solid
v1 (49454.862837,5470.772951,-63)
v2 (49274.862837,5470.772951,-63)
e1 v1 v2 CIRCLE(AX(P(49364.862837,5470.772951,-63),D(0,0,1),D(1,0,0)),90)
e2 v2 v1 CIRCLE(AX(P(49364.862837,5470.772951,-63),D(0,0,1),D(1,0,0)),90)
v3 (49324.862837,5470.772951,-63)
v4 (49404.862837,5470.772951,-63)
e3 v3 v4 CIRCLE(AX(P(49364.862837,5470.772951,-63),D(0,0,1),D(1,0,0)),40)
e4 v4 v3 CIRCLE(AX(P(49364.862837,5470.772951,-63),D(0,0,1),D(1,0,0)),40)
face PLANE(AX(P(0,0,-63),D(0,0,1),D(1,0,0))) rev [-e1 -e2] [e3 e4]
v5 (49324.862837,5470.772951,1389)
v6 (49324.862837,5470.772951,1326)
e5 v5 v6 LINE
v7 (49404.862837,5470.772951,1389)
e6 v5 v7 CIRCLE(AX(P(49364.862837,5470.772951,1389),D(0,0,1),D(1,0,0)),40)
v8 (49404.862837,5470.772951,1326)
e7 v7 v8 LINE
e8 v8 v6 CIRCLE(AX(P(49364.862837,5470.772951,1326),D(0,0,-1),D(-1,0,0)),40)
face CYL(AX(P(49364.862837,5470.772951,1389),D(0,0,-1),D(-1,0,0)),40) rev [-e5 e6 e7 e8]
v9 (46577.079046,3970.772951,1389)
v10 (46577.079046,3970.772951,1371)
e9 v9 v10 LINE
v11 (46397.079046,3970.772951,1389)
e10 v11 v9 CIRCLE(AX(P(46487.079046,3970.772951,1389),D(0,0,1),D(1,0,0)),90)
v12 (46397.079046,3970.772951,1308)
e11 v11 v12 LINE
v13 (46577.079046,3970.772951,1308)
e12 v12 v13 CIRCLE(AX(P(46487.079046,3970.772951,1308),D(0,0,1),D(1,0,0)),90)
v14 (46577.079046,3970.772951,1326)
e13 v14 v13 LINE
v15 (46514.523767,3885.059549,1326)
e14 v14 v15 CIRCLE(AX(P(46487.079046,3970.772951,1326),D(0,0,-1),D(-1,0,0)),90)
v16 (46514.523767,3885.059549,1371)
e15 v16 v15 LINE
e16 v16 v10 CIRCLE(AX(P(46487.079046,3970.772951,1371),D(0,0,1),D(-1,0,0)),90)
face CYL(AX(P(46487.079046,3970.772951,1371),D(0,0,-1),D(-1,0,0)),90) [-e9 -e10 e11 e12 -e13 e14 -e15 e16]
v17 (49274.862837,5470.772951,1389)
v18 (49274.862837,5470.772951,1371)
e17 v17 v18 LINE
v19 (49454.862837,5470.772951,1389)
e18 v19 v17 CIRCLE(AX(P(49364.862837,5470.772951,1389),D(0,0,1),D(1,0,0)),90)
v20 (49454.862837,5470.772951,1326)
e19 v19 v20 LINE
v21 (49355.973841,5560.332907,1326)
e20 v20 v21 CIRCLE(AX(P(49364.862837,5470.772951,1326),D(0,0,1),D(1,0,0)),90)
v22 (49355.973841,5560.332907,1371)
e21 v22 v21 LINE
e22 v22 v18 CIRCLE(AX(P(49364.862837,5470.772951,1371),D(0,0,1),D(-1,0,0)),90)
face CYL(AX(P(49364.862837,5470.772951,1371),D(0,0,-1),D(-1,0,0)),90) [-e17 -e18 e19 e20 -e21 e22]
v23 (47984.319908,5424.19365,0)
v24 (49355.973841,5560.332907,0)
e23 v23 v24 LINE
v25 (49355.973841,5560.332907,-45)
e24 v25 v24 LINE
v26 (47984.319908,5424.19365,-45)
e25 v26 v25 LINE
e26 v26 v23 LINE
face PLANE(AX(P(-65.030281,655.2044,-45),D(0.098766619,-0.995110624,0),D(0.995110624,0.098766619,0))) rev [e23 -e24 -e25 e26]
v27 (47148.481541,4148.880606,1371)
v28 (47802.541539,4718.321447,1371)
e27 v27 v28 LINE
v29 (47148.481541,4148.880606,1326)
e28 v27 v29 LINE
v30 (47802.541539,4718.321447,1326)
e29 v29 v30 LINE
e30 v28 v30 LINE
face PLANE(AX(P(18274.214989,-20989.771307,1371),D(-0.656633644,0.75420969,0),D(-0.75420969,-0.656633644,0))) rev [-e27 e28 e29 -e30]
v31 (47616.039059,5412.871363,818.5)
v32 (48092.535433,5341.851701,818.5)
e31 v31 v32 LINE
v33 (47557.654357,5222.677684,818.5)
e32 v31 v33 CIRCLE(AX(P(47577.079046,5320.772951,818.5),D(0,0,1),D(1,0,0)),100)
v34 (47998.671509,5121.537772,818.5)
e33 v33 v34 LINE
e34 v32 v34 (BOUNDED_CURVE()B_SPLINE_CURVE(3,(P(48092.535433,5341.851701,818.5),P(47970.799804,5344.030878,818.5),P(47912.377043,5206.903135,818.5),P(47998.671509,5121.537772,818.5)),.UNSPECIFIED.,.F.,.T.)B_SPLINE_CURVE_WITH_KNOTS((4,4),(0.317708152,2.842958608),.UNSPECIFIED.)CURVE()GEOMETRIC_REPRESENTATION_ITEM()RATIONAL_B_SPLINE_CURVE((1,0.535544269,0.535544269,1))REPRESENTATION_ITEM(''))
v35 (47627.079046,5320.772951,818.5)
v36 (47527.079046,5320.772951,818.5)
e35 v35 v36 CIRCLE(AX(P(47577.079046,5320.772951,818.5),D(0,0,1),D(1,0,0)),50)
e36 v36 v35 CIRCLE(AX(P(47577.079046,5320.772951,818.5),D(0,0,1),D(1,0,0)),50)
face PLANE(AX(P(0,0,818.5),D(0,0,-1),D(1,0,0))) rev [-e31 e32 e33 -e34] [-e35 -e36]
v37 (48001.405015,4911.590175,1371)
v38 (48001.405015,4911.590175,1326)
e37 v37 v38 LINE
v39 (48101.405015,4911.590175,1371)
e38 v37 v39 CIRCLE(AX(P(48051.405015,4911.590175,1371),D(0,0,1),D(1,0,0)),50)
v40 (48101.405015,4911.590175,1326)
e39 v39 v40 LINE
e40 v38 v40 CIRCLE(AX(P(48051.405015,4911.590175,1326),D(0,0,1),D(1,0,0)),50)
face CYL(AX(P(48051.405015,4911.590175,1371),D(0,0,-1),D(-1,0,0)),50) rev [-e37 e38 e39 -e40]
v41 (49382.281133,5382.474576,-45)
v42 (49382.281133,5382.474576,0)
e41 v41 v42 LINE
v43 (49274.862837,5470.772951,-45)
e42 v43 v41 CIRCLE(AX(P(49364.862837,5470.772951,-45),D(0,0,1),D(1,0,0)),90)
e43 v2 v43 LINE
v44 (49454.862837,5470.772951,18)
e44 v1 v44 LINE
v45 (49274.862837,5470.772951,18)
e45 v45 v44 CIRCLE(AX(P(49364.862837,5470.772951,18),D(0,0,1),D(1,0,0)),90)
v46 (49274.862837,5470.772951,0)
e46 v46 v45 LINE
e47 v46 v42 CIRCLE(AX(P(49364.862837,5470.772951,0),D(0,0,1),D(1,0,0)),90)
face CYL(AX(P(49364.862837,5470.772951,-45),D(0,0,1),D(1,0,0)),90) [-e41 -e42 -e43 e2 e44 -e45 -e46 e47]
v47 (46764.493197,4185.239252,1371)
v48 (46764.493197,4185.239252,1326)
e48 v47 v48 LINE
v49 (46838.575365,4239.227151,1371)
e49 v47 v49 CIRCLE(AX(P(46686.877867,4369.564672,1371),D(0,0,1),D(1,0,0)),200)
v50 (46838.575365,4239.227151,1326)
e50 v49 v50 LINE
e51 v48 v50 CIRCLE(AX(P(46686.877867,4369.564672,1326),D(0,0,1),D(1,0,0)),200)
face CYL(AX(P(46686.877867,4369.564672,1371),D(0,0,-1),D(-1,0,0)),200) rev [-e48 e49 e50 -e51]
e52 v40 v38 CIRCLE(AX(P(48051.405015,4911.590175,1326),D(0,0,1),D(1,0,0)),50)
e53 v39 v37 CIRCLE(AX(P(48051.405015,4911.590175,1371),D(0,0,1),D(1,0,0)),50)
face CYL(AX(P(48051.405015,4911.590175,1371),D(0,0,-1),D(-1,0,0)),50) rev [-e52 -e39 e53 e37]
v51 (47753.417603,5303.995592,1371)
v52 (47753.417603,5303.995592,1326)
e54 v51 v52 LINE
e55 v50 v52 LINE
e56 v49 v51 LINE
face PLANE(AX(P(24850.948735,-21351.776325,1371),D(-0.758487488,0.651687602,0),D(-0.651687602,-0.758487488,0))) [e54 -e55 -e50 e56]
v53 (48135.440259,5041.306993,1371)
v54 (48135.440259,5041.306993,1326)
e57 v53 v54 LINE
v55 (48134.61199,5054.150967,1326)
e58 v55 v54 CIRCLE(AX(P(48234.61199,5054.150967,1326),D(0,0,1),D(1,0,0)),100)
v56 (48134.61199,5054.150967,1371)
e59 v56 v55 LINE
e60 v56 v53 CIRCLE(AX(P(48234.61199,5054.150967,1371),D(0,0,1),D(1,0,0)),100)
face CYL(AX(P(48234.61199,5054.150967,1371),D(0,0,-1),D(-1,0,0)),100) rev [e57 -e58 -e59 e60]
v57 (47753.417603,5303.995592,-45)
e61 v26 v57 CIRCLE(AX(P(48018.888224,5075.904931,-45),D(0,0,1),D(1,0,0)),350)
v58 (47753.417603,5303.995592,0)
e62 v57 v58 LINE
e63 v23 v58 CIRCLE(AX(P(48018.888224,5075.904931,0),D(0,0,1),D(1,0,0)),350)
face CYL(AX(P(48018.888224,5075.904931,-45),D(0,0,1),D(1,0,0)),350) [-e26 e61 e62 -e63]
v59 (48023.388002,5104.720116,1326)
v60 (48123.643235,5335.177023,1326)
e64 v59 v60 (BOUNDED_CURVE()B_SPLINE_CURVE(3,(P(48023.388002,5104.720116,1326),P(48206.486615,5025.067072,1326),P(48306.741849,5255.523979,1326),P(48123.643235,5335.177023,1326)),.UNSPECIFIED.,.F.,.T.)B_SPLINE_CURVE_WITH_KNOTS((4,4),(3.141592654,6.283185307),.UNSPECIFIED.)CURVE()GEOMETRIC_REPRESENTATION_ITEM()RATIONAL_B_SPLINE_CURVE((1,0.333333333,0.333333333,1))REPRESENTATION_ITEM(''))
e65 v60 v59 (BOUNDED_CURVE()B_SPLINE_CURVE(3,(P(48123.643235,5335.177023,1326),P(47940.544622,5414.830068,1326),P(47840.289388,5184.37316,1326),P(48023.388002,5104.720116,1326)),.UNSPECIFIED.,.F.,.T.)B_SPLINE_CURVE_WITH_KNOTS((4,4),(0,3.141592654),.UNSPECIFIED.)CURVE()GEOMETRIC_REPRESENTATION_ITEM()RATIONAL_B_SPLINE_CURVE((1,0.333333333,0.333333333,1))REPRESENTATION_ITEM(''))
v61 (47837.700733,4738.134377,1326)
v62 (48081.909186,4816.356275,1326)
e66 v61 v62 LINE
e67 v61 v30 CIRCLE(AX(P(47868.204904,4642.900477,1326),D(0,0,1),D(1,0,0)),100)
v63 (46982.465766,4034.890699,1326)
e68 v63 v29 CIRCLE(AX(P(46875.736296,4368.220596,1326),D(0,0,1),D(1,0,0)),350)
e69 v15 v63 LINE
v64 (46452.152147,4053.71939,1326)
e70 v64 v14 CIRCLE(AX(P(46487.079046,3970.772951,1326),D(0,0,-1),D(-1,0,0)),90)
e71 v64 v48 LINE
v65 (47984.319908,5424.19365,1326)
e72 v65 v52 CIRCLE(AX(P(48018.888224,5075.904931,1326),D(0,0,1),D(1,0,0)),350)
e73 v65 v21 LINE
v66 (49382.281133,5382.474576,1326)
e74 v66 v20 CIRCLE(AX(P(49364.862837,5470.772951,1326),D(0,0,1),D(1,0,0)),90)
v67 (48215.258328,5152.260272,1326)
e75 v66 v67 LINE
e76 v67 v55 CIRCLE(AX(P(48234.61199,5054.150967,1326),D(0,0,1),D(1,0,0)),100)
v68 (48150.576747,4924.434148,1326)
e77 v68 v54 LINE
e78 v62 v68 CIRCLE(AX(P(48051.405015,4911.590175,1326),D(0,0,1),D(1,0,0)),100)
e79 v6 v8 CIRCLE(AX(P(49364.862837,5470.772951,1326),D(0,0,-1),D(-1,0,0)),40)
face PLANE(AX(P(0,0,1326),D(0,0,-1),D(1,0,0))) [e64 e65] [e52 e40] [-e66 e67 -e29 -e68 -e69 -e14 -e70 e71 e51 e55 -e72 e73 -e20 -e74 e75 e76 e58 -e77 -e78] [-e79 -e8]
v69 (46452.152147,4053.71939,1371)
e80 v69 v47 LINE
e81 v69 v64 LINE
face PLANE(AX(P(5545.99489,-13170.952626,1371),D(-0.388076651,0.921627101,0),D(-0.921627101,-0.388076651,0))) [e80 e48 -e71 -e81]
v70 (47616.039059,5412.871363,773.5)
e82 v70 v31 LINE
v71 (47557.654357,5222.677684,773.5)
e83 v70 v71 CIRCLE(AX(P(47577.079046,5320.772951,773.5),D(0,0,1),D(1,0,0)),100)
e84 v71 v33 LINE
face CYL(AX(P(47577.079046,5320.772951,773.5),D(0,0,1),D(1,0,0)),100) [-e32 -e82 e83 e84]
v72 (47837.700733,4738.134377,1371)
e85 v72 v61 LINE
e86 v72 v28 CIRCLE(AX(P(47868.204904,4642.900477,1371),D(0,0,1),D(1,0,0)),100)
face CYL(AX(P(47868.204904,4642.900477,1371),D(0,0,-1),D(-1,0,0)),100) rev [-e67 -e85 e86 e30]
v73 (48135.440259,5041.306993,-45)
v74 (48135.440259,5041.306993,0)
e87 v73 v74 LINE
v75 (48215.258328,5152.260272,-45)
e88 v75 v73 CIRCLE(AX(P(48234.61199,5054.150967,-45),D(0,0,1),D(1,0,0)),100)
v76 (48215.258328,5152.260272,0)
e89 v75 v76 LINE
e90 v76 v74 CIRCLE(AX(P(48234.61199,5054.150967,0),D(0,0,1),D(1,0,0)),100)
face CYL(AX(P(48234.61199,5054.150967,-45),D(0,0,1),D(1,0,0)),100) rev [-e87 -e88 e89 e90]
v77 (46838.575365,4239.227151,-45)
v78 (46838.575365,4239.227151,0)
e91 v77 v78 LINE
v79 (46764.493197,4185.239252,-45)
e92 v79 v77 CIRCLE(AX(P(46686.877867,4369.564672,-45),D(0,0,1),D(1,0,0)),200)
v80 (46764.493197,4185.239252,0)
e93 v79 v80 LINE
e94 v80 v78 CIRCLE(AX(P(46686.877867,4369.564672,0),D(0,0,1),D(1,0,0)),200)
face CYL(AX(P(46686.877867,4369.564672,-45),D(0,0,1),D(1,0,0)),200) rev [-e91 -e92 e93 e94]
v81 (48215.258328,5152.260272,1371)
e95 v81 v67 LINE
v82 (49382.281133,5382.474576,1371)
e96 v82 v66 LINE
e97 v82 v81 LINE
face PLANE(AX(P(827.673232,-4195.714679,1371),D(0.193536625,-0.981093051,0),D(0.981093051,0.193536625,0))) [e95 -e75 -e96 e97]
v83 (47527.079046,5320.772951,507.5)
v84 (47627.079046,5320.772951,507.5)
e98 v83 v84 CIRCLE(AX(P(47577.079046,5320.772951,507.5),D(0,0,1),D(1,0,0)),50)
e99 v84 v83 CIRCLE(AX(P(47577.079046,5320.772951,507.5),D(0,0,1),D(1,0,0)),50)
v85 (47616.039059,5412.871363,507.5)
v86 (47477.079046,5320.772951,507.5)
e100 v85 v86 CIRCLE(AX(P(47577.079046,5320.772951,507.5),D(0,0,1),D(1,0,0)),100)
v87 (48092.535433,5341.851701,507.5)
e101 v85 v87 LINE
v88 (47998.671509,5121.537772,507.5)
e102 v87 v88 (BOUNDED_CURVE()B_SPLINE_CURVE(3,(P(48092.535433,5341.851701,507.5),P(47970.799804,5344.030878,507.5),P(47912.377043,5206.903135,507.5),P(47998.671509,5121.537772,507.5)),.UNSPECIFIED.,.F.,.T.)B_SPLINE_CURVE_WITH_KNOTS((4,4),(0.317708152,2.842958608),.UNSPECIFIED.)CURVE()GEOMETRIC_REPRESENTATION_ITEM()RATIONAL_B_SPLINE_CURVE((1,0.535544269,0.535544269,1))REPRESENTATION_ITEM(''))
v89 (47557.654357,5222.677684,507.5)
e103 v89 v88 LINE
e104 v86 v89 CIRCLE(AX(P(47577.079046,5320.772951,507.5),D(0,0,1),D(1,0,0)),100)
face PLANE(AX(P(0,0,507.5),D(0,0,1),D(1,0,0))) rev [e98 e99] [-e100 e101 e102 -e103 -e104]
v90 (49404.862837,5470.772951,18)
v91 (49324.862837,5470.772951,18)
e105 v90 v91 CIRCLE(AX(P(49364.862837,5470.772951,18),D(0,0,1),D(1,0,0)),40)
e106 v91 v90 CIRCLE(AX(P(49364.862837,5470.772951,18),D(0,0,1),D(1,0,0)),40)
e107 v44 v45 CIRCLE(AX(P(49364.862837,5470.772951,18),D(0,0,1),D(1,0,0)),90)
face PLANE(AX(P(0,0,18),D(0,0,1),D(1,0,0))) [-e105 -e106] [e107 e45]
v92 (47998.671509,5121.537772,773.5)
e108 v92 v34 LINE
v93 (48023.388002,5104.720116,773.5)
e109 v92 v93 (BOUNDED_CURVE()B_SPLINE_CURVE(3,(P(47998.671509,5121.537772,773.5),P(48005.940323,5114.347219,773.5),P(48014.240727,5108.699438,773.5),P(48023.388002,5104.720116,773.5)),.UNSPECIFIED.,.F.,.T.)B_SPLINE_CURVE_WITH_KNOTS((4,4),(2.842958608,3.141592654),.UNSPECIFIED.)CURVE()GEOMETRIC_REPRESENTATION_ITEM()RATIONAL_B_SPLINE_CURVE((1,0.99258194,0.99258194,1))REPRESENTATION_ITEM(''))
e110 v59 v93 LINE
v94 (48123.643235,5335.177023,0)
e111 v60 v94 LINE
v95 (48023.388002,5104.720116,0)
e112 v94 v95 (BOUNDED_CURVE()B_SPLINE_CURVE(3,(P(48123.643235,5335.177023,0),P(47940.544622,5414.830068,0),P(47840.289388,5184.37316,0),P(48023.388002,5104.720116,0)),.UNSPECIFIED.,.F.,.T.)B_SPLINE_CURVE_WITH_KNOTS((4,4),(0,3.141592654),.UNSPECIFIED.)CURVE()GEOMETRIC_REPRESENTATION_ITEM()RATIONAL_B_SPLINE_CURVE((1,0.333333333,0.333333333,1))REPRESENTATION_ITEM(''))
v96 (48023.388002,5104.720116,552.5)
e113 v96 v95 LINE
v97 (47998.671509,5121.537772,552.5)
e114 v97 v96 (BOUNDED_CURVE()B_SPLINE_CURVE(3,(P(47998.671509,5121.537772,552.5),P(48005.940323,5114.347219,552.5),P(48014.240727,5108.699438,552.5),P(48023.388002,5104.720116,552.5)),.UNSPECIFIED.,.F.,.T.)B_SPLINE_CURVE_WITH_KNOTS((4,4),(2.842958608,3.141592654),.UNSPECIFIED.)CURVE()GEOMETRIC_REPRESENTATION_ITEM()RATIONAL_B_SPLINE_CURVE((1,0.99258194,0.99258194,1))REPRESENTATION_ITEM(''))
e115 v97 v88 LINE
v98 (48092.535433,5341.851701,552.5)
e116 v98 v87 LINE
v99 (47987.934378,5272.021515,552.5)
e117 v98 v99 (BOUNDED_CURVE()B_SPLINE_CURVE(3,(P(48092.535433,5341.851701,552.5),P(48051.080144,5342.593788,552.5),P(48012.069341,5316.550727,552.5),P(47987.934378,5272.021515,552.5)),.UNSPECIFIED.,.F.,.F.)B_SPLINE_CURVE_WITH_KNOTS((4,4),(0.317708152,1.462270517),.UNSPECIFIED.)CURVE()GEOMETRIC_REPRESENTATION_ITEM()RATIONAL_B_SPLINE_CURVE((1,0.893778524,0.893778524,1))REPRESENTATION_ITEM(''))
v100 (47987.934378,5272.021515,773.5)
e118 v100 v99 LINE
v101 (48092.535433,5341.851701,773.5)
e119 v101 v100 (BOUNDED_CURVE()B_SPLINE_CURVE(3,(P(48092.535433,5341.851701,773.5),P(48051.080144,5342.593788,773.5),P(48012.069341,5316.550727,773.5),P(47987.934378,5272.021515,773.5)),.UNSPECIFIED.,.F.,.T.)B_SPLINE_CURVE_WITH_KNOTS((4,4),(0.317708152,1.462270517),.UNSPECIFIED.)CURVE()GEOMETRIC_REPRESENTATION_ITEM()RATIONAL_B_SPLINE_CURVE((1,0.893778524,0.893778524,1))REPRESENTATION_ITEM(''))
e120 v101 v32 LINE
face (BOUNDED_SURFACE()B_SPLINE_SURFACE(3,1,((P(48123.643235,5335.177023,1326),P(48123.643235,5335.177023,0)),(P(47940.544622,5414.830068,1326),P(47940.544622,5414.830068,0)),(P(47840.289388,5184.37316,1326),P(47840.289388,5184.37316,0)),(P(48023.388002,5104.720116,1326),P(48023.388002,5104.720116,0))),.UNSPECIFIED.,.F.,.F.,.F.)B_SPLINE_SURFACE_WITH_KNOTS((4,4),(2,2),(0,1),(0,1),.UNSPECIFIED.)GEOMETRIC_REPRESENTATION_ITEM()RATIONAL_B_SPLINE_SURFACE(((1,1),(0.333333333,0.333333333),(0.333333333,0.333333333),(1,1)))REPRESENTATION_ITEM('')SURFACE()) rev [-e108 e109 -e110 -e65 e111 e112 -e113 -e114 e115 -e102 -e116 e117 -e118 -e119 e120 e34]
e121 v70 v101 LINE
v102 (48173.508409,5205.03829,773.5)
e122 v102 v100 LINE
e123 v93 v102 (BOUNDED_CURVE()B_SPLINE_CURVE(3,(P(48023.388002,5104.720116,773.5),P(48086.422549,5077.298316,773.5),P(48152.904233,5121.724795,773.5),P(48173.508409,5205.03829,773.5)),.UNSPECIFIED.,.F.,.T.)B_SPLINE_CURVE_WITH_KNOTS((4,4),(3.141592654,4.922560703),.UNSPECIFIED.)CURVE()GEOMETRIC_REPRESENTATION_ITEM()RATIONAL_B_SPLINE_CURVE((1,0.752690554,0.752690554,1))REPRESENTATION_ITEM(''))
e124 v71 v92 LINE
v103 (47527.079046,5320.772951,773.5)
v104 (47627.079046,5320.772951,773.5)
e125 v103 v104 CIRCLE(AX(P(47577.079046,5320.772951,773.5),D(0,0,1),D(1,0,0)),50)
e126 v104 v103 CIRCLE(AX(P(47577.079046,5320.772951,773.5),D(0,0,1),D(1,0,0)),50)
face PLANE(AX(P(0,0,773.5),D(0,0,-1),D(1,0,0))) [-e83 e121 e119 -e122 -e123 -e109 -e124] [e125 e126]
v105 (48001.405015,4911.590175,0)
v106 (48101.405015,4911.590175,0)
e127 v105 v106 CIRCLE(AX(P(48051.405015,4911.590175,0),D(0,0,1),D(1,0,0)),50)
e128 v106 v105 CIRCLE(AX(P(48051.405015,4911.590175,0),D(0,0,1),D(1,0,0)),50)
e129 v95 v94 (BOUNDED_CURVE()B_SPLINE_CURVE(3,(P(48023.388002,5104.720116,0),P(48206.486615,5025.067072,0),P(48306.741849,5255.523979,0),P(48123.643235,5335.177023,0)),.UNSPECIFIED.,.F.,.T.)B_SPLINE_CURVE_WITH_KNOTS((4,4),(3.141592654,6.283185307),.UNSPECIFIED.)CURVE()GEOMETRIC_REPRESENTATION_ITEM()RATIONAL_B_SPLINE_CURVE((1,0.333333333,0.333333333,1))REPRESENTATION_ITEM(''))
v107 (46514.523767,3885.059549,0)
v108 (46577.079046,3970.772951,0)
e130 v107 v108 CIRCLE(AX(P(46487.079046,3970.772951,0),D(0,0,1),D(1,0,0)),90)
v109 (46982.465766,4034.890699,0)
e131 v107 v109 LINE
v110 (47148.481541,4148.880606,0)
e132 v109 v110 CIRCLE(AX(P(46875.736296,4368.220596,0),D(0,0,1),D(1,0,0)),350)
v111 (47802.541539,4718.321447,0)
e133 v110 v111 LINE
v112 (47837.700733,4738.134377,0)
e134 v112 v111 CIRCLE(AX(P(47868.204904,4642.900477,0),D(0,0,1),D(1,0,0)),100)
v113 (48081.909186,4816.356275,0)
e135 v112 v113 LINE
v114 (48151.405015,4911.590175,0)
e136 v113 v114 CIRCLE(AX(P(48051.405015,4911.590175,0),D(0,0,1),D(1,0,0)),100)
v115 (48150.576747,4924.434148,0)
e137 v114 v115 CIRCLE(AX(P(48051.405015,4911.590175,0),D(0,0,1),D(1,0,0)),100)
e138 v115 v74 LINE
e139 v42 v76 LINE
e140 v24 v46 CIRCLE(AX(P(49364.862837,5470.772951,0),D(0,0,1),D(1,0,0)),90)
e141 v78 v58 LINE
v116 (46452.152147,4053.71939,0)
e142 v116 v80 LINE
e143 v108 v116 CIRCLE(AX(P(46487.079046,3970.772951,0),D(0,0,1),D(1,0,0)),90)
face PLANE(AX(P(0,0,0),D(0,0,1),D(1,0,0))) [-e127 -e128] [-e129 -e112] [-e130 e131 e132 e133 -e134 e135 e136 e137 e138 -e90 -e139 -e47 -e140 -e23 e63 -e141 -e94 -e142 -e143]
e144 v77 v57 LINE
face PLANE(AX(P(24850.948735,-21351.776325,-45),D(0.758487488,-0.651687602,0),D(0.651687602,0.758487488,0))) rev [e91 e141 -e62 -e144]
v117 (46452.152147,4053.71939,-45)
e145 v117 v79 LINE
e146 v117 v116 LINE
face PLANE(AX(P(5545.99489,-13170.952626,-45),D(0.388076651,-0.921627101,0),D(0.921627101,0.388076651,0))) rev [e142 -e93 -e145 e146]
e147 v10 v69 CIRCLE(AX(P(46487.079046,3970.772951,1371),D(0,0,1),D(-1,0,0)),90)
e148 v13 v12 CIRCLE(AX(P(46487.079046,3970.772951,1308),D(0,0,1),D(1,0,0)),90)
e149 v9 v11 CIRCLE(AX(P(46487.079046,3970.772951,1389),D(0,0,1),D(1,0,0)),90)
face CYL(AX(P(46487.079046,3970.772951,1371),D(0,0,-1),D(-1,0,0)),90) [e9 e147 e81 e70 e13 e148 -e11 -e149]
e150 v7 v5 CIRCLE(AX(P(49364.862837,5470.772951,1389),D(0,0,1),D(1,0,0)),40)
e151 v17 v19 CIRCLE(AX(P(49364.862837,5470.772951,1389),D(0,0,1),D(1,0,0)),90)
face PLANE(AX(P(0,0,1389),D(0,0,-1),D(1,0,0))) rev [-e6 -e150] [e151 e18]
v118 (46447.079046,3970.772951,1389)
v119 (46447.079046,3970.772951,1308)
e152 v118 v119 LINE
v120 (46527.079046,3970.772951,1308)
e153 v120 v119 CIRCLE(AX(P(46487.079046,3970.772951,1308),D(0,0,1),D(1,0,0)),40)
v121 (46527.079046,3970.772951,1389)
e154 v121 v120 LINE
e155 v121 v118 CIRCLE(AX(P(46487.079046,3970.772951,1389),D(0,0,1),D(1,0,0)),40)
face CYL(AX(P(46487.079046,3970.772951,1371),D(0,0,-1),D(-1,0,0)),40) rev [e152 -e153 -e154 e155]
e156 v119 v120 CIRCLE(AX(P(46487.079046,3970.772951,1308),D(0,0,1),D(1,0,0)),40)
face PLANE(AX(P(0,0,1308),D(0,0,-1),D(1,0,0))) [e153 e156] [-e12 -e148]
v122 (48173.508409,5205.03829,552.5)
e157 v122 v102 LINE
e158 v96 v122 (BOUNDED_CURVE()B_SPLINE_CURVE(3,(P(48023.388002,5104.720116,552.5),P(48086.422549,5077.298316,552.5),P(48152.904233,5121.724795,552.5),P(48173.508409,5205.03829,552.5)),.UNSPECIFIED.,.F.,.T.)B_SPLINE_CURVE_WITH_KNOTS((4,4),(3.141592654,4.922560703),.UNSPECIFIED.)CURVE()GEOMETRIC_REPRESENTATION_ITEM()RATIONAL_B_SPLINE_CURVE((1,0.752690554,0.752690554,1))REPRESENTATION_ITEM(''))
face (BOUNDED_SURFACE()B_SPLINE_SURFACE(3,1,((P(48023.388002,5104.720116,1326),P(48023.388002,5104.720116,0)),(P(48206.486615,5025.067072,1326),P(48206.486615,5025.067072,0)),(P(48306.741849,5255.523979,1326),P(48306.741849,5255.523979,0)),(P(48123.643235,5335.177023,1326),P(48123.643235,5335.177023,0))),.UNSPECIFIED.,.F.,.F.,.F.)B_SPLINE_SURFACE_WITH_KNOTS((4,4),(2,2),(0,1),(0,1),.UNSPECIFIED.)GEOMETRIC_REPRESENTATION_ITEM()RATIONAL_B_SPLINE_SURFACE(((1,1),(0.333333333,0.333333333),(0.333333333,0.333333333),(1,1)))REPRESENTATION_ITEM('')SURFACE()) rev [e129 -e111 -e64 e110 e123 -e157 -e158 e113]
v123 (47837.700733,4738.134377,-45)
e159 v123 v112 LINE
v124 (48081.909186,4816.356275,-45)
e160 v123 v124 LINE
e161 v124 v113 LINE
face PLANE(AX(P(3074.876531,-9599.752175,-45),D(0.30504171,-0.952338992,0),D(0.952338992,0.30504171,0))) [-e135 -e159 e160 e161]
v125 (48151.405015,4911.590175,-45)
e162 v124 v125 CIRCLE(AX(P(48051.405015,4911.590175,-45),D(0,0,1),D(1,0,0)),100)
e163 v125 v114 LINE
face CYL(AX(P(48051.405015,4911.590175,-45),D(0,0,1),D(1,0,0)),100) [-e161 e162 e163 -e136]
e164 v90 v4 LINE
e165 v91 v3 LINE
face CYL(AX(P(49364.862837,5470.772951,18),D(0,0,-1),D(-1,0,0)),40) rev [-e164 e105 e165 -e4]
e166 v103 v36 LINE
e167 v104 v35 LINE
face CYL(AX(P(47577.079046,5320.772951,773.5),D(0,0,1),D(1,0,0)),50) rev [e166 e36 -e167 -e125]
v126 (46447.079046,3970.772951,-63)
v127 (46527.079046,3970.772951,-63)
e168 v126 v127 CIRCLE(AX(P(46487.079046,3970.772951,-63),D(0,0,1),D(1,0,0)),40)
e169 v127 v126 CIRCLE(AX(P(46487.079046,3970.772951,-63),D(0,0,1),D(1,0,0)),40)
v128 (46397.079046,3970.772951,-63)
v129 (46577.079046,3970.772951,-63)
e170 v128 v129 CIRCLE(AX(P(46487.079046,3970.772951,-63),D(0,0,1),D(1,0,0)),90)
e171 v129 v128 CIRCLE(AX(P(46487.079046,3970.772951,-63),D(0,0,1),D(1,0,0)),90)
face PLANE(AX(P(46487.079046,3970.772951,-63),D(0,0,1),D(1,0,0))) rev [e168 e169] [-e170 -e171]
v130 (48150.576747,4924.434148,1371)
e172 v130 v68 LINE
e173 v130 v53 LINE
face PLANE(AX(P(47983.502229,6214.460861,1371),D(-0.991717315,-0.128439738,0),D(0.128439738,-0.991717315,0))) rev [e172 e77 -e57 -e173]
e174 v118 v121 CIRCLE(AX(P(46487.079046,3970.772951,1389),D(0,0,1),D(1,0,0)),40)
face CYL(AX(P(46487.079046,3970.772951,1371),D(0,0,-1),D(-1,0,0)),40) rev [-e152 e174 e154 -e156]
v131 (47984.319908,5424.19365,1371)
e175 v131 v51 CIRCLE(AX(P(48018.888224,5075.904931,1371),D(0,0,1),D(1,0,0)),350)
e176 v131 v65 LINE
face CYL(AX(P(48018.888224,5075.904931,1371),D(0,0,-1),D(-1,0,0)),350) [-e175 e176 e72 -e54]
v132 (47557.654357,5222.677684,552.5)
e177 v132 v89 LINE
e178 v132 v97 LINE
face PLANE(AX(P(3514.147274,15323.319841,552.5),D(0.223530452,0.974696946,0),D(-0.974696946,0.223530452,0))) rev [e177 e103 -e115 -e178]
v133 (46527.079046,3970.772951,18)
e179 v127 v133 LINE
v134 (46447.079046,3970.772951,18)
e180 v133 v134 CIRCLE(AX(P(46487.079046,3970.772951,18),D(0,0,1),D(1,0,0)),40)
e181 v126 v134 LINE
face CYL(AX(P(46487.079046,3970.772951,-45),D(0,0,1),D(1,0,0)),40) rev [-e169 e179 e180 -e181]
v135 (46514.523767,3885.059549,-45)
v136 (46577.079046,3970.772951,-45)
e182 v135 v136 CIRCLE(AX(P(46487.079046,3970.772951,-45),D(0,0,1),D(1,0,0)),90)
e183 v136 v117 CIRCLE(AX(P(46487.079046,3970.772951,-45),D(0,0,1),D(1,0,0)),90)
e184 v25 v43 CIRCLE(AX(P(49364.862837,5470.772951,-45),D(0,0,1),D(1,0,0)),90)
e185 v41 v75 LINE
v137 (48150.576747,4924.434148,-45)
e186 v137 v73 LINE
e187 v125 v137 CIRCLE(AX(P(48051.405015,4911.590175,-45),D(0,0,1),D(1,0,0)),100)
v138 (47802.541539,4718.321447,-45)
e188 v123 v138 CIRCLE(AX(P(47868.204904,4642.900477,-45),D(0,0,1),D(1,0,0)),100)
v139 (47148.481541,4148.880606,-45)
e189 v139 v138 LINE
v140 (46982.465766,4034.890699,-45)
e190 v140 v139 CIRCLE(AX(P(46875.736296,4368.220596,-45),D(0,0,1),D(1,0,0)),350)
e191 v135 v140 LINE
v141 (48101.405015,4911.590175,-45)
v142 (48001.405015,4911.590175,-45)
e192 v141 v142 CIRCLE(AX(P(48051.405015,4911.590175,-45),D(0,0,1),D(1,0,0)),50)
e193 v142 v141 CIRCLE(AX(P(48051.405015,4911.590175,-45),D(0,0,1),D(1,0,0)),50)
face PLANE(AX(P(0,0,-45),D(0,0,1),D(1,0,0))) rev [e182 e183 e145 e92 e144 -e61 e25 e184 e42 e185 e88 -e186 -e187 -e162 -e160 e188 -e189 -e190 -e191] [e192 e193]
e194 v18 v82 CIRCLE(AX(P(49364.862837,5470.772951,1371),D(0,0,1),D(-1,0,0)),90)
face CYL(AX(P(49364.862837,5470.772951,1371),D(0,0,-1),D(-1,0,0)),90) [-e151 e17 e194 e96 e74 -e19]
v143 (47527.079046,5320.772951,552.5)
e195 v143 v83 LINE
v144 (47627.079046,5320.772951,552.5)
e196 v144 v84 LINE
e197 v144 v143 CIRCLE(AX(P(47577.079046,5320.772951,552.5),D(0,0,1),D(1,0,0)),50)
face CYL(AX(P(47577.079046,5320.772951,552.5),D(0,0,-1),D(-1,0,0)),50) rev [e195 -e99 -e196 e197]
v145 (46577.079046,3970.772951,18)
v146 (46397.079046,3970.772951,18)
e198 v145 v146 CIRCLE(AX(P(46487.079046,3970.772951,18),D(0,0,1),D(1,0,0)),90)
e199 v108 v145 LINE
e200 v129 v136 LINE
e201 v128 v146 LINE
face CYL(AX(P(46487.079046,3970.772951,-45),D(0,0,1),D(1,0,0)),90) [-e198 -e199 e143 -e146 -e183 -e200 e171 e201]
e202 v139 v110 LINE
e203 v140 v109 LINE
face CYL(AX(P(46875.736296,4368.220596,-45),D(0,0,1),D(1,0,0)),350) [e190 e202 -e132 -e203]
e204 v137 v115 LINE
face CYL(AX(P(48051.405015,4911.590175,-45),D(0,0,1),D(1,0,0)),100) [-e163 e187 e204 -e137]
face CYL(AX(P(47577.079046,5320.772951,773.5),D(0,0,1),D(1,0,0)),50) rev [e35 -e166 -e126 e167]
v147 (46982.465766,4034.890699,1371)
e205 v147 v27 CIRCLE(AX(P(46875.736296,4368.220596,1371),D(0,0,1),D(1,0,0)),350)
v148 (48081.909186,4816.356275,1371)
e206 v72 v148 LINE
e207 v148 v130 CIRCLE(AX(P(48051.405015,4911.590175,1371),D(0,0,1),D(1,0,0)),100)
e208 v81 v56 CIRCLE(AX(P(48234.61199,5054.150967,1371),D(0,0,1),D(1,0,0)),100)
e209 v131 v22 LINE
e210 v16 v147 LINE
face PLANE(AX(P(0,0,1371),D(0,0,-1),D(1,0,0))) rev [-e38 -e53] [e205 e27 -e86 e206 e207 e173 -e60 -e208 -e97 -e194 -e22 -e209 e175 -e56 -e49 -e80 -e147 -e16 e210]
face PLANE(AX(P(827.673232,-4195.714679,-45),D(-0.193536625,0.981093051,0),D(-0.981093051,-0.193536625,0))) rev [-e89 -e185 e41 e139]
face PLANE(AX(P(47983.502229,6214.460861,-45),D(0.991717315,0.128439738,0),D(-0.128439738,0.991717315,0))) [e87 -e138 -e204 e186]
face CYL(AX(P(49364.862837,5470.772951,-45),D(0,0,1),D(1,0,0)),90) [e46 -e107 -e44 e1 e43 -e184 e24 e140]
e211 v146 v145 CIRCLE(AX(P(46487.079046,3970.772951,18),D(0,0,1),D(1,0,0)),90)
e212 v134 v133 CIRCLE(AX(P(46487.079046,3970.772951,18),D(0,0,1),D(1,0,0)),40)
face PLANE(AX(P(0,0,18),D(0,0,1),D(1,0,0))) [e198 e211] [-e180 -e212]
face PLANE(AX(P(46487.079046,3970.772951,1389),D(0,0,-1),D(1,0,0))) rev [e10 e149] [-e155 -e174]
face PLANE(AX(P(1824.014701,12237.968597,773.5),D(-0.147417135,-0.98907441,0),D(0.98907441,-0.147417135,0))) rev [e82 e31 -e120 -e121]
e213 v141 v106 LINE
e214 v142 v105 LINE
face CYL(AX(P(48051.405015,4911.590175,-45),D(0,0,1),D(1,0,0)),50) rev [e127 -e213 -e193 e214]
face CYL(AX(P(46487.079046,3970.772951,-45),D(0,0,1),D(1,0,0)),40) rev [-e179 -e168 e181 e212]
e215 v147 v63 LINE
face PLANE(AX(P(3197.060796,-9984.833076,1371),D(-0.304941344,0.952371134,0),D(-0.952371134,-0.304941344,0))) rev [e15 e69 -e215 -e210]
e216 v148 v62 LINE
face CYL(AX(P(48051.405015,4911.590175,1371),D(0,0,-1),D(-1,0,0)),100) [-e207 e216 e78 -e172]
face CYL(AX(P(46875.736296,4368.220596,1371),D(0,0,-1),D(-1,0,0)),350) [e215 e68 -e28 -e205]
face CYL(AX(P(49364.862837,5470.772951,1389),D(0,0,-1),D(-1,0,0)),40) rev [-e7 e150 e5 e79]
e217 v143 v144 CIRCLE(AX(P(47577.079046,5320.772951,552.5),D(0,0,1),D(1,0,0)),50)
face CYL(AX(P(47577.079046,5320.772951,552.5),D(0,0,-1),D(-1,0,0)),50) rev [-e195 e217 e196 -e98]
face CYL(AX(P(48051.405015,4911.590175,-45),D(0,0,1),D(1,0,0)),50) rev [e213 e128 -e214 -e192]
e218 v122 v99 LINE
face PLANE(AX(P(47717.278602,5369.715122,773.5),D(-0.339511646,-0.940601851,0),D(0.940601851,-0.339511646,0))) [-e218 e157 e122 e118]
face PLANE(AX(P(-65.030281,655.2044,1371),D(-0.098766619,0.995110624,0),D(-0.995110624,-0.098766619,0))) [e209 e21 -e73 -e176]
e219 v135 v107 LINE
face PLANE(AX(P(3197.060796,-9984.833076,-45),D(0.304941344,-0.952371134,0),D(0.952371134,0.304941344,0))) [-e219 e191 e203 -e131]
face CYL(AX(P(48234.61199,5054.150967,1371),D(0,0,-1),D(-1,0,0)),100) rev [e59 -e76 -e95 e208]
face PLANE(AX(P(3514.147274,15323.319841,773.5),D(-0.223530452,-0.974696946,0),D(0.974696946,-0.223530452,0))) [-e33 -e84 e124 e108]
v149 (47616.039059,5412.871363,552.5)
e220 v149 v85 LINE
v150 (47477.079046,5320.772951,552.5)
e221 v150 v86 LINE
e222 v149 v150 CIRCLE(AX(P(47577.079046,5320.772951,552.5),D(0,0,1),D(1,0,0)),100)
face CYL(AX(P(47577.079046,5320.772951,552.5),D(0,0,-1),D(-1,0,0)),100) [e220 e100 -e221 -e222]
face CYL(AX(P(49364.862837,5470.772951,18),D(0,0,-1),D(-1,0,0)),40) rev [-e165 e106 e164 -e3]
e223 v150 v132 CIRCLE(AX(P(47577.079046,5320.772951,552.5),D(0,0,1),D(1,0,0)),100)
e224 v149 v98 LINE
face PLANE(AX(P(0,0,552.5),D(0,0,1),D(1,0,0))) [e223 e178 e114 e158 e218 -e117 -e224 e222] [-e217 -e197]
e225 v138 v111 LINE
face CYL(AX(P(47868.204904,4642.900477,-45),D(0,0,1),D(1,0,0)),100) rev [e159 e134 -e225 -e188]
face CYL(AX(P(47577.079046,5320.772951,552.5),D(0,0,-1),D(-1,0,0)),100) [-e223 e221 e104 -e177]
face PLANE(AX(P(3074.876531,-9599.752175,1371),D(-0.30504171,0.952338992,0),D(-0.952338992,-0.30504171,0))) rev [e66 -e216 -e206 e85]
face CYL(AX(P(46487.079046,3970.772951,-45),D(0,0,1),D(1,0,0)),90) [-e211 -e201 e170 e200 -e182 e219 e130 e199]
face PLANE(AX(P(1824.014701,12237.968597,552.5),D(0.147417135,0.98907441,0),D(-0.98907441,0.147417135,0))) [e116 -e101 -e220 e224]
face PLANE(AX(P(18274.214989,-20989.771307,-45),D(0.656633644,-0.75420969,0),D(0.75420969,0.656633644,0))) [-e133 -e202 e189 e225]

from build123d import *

# Parameters (mm, degrees)
SKETCH_1_9_R        = 40
SKETCH_1_9_R_2      = 50
BOSS_EXTRUDE1_DEPTH = 45
BOSS_EXTRUDE2_START = 18
SKETCH_1_4_R        = 90
SKETCH_1_4_R_2      = 40
BOSS_EXTRUDE2_DEPTH = 18
BOSS_EXTRUDE3_START = 18
SKETCH_1_5_R        = 90
SKETCH_1_5_R_2      = 40
BOSS_EXTRUDE3_DEPTH = 18
SKETCH_1_6_R        = 90
SKETCH_1_6_R_2      = 40
BOSS_EXTRUDE4_DEPTH = 63
SKETCH_1_7_R        = 90
BOSS_EXTRUDE5_DEPTH = 63
SKETCH_1_8_RX       = 125.659756877
SKETCH_1_8_RY       = 99.837004296
BOSS_EXTRUDE6_DEPTH = 663
BOSS_EXTRUDE7_START = 552.5
SKETCH_1_9_2_R      = 100
SKETCH_1_9_2_R_2    = 50
BOSS_EXTRUDE7_DEPTH = 45
SKETCH2_R           = 40
CUT_EXTRUDE1_DEPTH  = 49788.688820018
SKETCH3_R           = 40
CUT_EXTRUDE2_DEPTH  = 49788.688820018
CUT_EXTRUDE3_DEPTH  = 221


with BuildPart() as part:
    # Sketch 1_9 → Boss-Extrude1 (new body)
    with BuildSketch(Plane.XY):
        with BuildLine():
            Line((46764.493197331, 4185.239251674), (46452.152147493, 4053.719390084))
            ThreePointArc((46452.152147493, 4053.719390084), (46402.66618426, 3939.556468955), (46514.523767059, 3885.059548967))
            Line((46514.523767059, 3885.059548967), (46982.465765958, 4034.890698674))
            ThreePointArc((46982.465765958, 4034.890698674), (47073.849116266, 4079.687564008), (47148.481541029, 4148.880605792))
            Line((47148.481541029, 4148.880605792), (47802.541539098, 4718.321446539))
            ThreePointArc((47802.541539098, 4718.321446539), (47819.111250519, 4730.020011667), (47837.700732572, 4738.134376685))
            Line((47837.700732572, 4738.134376685), (48081.909186186, 4816.356275444))
            ThreePointArc((48081.909186186, 4816.356275444), (48135.809793395, 4857.963377024), (48150.576746765, 4924.434148403))
            Line((48150.576746765, 4924.434148403), (48135.440258517, 5041.30699285))
            ThreePointArc((48135.440258517, 5041.30699285), (48153.434870258, 5112.548528391), (48215.258327605, 5152.260271737))
            Line((48215.258327605, 5152.260271737), (49382.281133207, 5382.474576425))
            ThreePointArc((49382.281133207, 5382.474576425), (49453.894200575, 5483.941713279), (49355.973841273, 5560.332907228))
            Line((49355.973841273, 5560.332907228), (47984.319907502, 5424.193649598))
            ThreePointArc((47984.319907502, 5424.193649598), (47857.278403088, 5386.359864507), (47753.417603416, 5303.995591733))
            Line((47753.417603416, 5303.995591733), (46838.575364644, 4239.227151402))
            ThreePointArc((46838.575364644, 4239.227151402), (46804.669066153, 4207.931651), (46764.493197331, 4185.239251674))
        make_face()
        with Locations((46487.079046119, 3970.772951026)):
            Circle(SKETCH_1_9_R, mode=Mode.SUBTRACT)
        with Locations((48051.40501522, 4911.590174628)):
            Circle(SKETCH_1_9_R_2, mode=Mode.SUBTRACT)
    boss_extrude1 = extrude(amount=-BOSS_EXTRUDE1_DEPTH)

    # 草图1<4> → Boss-Extrude2 (add)
    with BuildSketch(Plane.XY.offset(BOSS_EXTRUDE2_START)):
        with Locations((46487.079046119, 3970.772951026)):
            Circle(SKETCH_1_4_R)
        with Locations((46487.079046119, 3970.772951026)):
            Circle(SKETCH_1_4_R_2, mode=Mode.SUBTRACT)
    boss_extrude2 = extrude(amount=-BOSS_EXTRUDE2_DEPTH)

    # 草图1<5> → Boss-Extrude3 (add)
    with BuildSketch(Plane.XY.offset(BOSS_EXTRUDE3_START)):
        with Locations((49364.862836996, 5470.772951026)):
            Circle(SKETCH_1_5_R)
        with Locations((49364.862836996, 5470.772951026)):
            Circle(SKETCH_1_5_R_2, mode=Mode.SUBTRACT)
    extrude(amount=-BOSS_EXTRUDE3_DEPTH)

    # 草图1<6> → Boss-Extrude4 (add)
    with BuildSketch(Plane.XY):
        with Locations((49364.862836996, 5470.772951026)):
            Circle(SKETCH_1_6_R)
        with Locations((49364.862836996, 5470.772951026)):
            Circle(SKETCH_1_6_R_2, mode=Mode.SUBTRACT)
    boss_extrude4 = extrude(amount=-BOSS_EXTRUDE4_DEPTH)

    # 草图1<7> → Boss-Extrude5 (add)
    with BuildSketch(Plane.XY):
        with Locations((46487.079046119, 3970.772951026)):
            Circle(SKETCH_1_7_R)
    boss_extrude5 = extrude(amount=-BOSS_EXTRUDE5_DEPTH)

    # 草图1<8> → Boss-Extrude6 (add)
    with BuildSketch(Plane.XY):
        with Locations(Location((48073.515618599, 5219.948569609), (0, 0, 66.489605314))):
            Ellipse(SKETCH_1_8_RX, SKETCH_1_8_RY)
    boss_extrude6 = extrude(amount=BOSS_EXTRUDE6_DEPTH)

    # Sketch 1_9 2 → Boss-Extrude7 (add)
    # profile 1 of 3: a face of its own
    with BuildSketch(Plane.XY.offset(BOSS_EXTRUDE7_START)):
        with BuildLine():
            Line((47557.654356915, 5222.677683814), (47662.826482923, 5198.558214679))
            Line((47662.826482923, 5198.558214679), (47753.417603416, 5303.995591733))
            ThreePointArc((47753.417603416, 5303.995591733), (47795.418981849, 5345.277345585), (47843.747365572, 5378.932453937))
            Line((47843.747365572, 5378.932453937), (47616.039058549, 5412.871362692))
            ThreePointArc((47616.039058549, 5412.871362692), (47660.433713784, 5376.017854668), (47677.079046119, 5320.772951026))
            ThreePointArc((47677.079046119, 5320.772951026), (47640.551603494, 5243.499187948), (47557.654356915, 5222.677683814))
        make_face()
    # profile 2 of 3: a face of its own
    with BuildSketch(Plane.XY.offset(BOSS_EXTRUDE7_START)):
        with Locations((47577.079046119, 5320.772951026)):
            Circle(SKETCH_1_9_2_R)
        with Locations(Location((47577.079046119, 5320.772951026, 0), (0, 0, 180))):
            Circle(SKETCH_1_9_2_R_2, mode=Mode.SUBTRACT)
    # profile 3 of 3: a face of its own
    with BuildSketch(Plane.XY.offset(BOSS_EXTRUDE7_START)):
        with BuildLine():
            Line((47753.417603416, 5303.995591733), (47662.826482923, 5198.558214679))
            Line((47662.826482923, 5198.558214679), (47998.671509076, 5121.53777162))
            add(Edge.make_bspline(
                [(48092.5354326, 5341.85170086), (47770.125479059, 5347.623127791), (47998.671509076, 5121.53777162)],
                knots=[0.317708152, 0.317708152, 0.317708152, 2.842958608, 2.842958608, 2.842958608], degree=2, weights=[1, 0.303316403, 1]))
            Line((48092.5354326, 5341.85170086), (47843.747365572, 5378.932453937))
            ThreePointArc((47843.747365572, 5378.932453937), (47795.418981849, 5345.277345585), (47753.417603416, 5303.995591733))
        make_face()
    boss_extrude7 = extrude(amount=-BOSS_EXTRUDE7_DEPTH)

    # Mirror1: Boss-Extrude6, Boss-Extrude7 across plane
    add(boss_extrude6.mirror(Plane.XY.offset(663)))
    add(boss_extrude7.mirror(Plane.XY.offset(663)))

    # Mirror2: Boss-Extrude1, Boss-Extrude2, Boss-Extrude4, Boss-Extrude5 across plane
    add(boss_extrude1.mirror(Plane.XY.offset(663)))
    add(boss_extrude2.mirror(Plane.XY.offset(663)))
    add(boss_extrude4.mirror(Plane.XY.offset(663)))
    add(boss_extrude5.mirror(Plane.XY.offset(663)))

    # Sketch2 → Cut-Extrude1 (cut, through all)
    with BuildSketch(Plane.XY.offset(1389)):
        with Locations((49364.862836996, 5470.772951026)):
            Circle(SKETCH2_R)
    extrude(amount=-CUT_EXTRUDE1_DEPTH, mode=Mode.SUBTRACT)

    # Sketch3 → Cut-Extrude2 (cut, through all)
    with BuildSketch(Plane.XY.offset(1389)):
        with Locations((46487.079046119, 3970.772951026)):
            Circle(SKETCH3_R)
    extrude(amount=-CUT_EXTRUDE2_DEPTH, mode=Mode.SUBTRACT)

    # Sketch5 → Cut-Extrude3 (cut)
    with BuildSketch(Plane.XY.offset(552.5)):
        Polygon((47717.278601739, 5369.715122103), (48519.148514072, 5080.278976816), (48183.962905589, 4783.475969073), (47697.072231971, 5313.734277215), align=None)
    extrude(amount=CUT_EXTRUDE3_DEPTH, mode=Mode.SUBTRACT)


solid = part.part
